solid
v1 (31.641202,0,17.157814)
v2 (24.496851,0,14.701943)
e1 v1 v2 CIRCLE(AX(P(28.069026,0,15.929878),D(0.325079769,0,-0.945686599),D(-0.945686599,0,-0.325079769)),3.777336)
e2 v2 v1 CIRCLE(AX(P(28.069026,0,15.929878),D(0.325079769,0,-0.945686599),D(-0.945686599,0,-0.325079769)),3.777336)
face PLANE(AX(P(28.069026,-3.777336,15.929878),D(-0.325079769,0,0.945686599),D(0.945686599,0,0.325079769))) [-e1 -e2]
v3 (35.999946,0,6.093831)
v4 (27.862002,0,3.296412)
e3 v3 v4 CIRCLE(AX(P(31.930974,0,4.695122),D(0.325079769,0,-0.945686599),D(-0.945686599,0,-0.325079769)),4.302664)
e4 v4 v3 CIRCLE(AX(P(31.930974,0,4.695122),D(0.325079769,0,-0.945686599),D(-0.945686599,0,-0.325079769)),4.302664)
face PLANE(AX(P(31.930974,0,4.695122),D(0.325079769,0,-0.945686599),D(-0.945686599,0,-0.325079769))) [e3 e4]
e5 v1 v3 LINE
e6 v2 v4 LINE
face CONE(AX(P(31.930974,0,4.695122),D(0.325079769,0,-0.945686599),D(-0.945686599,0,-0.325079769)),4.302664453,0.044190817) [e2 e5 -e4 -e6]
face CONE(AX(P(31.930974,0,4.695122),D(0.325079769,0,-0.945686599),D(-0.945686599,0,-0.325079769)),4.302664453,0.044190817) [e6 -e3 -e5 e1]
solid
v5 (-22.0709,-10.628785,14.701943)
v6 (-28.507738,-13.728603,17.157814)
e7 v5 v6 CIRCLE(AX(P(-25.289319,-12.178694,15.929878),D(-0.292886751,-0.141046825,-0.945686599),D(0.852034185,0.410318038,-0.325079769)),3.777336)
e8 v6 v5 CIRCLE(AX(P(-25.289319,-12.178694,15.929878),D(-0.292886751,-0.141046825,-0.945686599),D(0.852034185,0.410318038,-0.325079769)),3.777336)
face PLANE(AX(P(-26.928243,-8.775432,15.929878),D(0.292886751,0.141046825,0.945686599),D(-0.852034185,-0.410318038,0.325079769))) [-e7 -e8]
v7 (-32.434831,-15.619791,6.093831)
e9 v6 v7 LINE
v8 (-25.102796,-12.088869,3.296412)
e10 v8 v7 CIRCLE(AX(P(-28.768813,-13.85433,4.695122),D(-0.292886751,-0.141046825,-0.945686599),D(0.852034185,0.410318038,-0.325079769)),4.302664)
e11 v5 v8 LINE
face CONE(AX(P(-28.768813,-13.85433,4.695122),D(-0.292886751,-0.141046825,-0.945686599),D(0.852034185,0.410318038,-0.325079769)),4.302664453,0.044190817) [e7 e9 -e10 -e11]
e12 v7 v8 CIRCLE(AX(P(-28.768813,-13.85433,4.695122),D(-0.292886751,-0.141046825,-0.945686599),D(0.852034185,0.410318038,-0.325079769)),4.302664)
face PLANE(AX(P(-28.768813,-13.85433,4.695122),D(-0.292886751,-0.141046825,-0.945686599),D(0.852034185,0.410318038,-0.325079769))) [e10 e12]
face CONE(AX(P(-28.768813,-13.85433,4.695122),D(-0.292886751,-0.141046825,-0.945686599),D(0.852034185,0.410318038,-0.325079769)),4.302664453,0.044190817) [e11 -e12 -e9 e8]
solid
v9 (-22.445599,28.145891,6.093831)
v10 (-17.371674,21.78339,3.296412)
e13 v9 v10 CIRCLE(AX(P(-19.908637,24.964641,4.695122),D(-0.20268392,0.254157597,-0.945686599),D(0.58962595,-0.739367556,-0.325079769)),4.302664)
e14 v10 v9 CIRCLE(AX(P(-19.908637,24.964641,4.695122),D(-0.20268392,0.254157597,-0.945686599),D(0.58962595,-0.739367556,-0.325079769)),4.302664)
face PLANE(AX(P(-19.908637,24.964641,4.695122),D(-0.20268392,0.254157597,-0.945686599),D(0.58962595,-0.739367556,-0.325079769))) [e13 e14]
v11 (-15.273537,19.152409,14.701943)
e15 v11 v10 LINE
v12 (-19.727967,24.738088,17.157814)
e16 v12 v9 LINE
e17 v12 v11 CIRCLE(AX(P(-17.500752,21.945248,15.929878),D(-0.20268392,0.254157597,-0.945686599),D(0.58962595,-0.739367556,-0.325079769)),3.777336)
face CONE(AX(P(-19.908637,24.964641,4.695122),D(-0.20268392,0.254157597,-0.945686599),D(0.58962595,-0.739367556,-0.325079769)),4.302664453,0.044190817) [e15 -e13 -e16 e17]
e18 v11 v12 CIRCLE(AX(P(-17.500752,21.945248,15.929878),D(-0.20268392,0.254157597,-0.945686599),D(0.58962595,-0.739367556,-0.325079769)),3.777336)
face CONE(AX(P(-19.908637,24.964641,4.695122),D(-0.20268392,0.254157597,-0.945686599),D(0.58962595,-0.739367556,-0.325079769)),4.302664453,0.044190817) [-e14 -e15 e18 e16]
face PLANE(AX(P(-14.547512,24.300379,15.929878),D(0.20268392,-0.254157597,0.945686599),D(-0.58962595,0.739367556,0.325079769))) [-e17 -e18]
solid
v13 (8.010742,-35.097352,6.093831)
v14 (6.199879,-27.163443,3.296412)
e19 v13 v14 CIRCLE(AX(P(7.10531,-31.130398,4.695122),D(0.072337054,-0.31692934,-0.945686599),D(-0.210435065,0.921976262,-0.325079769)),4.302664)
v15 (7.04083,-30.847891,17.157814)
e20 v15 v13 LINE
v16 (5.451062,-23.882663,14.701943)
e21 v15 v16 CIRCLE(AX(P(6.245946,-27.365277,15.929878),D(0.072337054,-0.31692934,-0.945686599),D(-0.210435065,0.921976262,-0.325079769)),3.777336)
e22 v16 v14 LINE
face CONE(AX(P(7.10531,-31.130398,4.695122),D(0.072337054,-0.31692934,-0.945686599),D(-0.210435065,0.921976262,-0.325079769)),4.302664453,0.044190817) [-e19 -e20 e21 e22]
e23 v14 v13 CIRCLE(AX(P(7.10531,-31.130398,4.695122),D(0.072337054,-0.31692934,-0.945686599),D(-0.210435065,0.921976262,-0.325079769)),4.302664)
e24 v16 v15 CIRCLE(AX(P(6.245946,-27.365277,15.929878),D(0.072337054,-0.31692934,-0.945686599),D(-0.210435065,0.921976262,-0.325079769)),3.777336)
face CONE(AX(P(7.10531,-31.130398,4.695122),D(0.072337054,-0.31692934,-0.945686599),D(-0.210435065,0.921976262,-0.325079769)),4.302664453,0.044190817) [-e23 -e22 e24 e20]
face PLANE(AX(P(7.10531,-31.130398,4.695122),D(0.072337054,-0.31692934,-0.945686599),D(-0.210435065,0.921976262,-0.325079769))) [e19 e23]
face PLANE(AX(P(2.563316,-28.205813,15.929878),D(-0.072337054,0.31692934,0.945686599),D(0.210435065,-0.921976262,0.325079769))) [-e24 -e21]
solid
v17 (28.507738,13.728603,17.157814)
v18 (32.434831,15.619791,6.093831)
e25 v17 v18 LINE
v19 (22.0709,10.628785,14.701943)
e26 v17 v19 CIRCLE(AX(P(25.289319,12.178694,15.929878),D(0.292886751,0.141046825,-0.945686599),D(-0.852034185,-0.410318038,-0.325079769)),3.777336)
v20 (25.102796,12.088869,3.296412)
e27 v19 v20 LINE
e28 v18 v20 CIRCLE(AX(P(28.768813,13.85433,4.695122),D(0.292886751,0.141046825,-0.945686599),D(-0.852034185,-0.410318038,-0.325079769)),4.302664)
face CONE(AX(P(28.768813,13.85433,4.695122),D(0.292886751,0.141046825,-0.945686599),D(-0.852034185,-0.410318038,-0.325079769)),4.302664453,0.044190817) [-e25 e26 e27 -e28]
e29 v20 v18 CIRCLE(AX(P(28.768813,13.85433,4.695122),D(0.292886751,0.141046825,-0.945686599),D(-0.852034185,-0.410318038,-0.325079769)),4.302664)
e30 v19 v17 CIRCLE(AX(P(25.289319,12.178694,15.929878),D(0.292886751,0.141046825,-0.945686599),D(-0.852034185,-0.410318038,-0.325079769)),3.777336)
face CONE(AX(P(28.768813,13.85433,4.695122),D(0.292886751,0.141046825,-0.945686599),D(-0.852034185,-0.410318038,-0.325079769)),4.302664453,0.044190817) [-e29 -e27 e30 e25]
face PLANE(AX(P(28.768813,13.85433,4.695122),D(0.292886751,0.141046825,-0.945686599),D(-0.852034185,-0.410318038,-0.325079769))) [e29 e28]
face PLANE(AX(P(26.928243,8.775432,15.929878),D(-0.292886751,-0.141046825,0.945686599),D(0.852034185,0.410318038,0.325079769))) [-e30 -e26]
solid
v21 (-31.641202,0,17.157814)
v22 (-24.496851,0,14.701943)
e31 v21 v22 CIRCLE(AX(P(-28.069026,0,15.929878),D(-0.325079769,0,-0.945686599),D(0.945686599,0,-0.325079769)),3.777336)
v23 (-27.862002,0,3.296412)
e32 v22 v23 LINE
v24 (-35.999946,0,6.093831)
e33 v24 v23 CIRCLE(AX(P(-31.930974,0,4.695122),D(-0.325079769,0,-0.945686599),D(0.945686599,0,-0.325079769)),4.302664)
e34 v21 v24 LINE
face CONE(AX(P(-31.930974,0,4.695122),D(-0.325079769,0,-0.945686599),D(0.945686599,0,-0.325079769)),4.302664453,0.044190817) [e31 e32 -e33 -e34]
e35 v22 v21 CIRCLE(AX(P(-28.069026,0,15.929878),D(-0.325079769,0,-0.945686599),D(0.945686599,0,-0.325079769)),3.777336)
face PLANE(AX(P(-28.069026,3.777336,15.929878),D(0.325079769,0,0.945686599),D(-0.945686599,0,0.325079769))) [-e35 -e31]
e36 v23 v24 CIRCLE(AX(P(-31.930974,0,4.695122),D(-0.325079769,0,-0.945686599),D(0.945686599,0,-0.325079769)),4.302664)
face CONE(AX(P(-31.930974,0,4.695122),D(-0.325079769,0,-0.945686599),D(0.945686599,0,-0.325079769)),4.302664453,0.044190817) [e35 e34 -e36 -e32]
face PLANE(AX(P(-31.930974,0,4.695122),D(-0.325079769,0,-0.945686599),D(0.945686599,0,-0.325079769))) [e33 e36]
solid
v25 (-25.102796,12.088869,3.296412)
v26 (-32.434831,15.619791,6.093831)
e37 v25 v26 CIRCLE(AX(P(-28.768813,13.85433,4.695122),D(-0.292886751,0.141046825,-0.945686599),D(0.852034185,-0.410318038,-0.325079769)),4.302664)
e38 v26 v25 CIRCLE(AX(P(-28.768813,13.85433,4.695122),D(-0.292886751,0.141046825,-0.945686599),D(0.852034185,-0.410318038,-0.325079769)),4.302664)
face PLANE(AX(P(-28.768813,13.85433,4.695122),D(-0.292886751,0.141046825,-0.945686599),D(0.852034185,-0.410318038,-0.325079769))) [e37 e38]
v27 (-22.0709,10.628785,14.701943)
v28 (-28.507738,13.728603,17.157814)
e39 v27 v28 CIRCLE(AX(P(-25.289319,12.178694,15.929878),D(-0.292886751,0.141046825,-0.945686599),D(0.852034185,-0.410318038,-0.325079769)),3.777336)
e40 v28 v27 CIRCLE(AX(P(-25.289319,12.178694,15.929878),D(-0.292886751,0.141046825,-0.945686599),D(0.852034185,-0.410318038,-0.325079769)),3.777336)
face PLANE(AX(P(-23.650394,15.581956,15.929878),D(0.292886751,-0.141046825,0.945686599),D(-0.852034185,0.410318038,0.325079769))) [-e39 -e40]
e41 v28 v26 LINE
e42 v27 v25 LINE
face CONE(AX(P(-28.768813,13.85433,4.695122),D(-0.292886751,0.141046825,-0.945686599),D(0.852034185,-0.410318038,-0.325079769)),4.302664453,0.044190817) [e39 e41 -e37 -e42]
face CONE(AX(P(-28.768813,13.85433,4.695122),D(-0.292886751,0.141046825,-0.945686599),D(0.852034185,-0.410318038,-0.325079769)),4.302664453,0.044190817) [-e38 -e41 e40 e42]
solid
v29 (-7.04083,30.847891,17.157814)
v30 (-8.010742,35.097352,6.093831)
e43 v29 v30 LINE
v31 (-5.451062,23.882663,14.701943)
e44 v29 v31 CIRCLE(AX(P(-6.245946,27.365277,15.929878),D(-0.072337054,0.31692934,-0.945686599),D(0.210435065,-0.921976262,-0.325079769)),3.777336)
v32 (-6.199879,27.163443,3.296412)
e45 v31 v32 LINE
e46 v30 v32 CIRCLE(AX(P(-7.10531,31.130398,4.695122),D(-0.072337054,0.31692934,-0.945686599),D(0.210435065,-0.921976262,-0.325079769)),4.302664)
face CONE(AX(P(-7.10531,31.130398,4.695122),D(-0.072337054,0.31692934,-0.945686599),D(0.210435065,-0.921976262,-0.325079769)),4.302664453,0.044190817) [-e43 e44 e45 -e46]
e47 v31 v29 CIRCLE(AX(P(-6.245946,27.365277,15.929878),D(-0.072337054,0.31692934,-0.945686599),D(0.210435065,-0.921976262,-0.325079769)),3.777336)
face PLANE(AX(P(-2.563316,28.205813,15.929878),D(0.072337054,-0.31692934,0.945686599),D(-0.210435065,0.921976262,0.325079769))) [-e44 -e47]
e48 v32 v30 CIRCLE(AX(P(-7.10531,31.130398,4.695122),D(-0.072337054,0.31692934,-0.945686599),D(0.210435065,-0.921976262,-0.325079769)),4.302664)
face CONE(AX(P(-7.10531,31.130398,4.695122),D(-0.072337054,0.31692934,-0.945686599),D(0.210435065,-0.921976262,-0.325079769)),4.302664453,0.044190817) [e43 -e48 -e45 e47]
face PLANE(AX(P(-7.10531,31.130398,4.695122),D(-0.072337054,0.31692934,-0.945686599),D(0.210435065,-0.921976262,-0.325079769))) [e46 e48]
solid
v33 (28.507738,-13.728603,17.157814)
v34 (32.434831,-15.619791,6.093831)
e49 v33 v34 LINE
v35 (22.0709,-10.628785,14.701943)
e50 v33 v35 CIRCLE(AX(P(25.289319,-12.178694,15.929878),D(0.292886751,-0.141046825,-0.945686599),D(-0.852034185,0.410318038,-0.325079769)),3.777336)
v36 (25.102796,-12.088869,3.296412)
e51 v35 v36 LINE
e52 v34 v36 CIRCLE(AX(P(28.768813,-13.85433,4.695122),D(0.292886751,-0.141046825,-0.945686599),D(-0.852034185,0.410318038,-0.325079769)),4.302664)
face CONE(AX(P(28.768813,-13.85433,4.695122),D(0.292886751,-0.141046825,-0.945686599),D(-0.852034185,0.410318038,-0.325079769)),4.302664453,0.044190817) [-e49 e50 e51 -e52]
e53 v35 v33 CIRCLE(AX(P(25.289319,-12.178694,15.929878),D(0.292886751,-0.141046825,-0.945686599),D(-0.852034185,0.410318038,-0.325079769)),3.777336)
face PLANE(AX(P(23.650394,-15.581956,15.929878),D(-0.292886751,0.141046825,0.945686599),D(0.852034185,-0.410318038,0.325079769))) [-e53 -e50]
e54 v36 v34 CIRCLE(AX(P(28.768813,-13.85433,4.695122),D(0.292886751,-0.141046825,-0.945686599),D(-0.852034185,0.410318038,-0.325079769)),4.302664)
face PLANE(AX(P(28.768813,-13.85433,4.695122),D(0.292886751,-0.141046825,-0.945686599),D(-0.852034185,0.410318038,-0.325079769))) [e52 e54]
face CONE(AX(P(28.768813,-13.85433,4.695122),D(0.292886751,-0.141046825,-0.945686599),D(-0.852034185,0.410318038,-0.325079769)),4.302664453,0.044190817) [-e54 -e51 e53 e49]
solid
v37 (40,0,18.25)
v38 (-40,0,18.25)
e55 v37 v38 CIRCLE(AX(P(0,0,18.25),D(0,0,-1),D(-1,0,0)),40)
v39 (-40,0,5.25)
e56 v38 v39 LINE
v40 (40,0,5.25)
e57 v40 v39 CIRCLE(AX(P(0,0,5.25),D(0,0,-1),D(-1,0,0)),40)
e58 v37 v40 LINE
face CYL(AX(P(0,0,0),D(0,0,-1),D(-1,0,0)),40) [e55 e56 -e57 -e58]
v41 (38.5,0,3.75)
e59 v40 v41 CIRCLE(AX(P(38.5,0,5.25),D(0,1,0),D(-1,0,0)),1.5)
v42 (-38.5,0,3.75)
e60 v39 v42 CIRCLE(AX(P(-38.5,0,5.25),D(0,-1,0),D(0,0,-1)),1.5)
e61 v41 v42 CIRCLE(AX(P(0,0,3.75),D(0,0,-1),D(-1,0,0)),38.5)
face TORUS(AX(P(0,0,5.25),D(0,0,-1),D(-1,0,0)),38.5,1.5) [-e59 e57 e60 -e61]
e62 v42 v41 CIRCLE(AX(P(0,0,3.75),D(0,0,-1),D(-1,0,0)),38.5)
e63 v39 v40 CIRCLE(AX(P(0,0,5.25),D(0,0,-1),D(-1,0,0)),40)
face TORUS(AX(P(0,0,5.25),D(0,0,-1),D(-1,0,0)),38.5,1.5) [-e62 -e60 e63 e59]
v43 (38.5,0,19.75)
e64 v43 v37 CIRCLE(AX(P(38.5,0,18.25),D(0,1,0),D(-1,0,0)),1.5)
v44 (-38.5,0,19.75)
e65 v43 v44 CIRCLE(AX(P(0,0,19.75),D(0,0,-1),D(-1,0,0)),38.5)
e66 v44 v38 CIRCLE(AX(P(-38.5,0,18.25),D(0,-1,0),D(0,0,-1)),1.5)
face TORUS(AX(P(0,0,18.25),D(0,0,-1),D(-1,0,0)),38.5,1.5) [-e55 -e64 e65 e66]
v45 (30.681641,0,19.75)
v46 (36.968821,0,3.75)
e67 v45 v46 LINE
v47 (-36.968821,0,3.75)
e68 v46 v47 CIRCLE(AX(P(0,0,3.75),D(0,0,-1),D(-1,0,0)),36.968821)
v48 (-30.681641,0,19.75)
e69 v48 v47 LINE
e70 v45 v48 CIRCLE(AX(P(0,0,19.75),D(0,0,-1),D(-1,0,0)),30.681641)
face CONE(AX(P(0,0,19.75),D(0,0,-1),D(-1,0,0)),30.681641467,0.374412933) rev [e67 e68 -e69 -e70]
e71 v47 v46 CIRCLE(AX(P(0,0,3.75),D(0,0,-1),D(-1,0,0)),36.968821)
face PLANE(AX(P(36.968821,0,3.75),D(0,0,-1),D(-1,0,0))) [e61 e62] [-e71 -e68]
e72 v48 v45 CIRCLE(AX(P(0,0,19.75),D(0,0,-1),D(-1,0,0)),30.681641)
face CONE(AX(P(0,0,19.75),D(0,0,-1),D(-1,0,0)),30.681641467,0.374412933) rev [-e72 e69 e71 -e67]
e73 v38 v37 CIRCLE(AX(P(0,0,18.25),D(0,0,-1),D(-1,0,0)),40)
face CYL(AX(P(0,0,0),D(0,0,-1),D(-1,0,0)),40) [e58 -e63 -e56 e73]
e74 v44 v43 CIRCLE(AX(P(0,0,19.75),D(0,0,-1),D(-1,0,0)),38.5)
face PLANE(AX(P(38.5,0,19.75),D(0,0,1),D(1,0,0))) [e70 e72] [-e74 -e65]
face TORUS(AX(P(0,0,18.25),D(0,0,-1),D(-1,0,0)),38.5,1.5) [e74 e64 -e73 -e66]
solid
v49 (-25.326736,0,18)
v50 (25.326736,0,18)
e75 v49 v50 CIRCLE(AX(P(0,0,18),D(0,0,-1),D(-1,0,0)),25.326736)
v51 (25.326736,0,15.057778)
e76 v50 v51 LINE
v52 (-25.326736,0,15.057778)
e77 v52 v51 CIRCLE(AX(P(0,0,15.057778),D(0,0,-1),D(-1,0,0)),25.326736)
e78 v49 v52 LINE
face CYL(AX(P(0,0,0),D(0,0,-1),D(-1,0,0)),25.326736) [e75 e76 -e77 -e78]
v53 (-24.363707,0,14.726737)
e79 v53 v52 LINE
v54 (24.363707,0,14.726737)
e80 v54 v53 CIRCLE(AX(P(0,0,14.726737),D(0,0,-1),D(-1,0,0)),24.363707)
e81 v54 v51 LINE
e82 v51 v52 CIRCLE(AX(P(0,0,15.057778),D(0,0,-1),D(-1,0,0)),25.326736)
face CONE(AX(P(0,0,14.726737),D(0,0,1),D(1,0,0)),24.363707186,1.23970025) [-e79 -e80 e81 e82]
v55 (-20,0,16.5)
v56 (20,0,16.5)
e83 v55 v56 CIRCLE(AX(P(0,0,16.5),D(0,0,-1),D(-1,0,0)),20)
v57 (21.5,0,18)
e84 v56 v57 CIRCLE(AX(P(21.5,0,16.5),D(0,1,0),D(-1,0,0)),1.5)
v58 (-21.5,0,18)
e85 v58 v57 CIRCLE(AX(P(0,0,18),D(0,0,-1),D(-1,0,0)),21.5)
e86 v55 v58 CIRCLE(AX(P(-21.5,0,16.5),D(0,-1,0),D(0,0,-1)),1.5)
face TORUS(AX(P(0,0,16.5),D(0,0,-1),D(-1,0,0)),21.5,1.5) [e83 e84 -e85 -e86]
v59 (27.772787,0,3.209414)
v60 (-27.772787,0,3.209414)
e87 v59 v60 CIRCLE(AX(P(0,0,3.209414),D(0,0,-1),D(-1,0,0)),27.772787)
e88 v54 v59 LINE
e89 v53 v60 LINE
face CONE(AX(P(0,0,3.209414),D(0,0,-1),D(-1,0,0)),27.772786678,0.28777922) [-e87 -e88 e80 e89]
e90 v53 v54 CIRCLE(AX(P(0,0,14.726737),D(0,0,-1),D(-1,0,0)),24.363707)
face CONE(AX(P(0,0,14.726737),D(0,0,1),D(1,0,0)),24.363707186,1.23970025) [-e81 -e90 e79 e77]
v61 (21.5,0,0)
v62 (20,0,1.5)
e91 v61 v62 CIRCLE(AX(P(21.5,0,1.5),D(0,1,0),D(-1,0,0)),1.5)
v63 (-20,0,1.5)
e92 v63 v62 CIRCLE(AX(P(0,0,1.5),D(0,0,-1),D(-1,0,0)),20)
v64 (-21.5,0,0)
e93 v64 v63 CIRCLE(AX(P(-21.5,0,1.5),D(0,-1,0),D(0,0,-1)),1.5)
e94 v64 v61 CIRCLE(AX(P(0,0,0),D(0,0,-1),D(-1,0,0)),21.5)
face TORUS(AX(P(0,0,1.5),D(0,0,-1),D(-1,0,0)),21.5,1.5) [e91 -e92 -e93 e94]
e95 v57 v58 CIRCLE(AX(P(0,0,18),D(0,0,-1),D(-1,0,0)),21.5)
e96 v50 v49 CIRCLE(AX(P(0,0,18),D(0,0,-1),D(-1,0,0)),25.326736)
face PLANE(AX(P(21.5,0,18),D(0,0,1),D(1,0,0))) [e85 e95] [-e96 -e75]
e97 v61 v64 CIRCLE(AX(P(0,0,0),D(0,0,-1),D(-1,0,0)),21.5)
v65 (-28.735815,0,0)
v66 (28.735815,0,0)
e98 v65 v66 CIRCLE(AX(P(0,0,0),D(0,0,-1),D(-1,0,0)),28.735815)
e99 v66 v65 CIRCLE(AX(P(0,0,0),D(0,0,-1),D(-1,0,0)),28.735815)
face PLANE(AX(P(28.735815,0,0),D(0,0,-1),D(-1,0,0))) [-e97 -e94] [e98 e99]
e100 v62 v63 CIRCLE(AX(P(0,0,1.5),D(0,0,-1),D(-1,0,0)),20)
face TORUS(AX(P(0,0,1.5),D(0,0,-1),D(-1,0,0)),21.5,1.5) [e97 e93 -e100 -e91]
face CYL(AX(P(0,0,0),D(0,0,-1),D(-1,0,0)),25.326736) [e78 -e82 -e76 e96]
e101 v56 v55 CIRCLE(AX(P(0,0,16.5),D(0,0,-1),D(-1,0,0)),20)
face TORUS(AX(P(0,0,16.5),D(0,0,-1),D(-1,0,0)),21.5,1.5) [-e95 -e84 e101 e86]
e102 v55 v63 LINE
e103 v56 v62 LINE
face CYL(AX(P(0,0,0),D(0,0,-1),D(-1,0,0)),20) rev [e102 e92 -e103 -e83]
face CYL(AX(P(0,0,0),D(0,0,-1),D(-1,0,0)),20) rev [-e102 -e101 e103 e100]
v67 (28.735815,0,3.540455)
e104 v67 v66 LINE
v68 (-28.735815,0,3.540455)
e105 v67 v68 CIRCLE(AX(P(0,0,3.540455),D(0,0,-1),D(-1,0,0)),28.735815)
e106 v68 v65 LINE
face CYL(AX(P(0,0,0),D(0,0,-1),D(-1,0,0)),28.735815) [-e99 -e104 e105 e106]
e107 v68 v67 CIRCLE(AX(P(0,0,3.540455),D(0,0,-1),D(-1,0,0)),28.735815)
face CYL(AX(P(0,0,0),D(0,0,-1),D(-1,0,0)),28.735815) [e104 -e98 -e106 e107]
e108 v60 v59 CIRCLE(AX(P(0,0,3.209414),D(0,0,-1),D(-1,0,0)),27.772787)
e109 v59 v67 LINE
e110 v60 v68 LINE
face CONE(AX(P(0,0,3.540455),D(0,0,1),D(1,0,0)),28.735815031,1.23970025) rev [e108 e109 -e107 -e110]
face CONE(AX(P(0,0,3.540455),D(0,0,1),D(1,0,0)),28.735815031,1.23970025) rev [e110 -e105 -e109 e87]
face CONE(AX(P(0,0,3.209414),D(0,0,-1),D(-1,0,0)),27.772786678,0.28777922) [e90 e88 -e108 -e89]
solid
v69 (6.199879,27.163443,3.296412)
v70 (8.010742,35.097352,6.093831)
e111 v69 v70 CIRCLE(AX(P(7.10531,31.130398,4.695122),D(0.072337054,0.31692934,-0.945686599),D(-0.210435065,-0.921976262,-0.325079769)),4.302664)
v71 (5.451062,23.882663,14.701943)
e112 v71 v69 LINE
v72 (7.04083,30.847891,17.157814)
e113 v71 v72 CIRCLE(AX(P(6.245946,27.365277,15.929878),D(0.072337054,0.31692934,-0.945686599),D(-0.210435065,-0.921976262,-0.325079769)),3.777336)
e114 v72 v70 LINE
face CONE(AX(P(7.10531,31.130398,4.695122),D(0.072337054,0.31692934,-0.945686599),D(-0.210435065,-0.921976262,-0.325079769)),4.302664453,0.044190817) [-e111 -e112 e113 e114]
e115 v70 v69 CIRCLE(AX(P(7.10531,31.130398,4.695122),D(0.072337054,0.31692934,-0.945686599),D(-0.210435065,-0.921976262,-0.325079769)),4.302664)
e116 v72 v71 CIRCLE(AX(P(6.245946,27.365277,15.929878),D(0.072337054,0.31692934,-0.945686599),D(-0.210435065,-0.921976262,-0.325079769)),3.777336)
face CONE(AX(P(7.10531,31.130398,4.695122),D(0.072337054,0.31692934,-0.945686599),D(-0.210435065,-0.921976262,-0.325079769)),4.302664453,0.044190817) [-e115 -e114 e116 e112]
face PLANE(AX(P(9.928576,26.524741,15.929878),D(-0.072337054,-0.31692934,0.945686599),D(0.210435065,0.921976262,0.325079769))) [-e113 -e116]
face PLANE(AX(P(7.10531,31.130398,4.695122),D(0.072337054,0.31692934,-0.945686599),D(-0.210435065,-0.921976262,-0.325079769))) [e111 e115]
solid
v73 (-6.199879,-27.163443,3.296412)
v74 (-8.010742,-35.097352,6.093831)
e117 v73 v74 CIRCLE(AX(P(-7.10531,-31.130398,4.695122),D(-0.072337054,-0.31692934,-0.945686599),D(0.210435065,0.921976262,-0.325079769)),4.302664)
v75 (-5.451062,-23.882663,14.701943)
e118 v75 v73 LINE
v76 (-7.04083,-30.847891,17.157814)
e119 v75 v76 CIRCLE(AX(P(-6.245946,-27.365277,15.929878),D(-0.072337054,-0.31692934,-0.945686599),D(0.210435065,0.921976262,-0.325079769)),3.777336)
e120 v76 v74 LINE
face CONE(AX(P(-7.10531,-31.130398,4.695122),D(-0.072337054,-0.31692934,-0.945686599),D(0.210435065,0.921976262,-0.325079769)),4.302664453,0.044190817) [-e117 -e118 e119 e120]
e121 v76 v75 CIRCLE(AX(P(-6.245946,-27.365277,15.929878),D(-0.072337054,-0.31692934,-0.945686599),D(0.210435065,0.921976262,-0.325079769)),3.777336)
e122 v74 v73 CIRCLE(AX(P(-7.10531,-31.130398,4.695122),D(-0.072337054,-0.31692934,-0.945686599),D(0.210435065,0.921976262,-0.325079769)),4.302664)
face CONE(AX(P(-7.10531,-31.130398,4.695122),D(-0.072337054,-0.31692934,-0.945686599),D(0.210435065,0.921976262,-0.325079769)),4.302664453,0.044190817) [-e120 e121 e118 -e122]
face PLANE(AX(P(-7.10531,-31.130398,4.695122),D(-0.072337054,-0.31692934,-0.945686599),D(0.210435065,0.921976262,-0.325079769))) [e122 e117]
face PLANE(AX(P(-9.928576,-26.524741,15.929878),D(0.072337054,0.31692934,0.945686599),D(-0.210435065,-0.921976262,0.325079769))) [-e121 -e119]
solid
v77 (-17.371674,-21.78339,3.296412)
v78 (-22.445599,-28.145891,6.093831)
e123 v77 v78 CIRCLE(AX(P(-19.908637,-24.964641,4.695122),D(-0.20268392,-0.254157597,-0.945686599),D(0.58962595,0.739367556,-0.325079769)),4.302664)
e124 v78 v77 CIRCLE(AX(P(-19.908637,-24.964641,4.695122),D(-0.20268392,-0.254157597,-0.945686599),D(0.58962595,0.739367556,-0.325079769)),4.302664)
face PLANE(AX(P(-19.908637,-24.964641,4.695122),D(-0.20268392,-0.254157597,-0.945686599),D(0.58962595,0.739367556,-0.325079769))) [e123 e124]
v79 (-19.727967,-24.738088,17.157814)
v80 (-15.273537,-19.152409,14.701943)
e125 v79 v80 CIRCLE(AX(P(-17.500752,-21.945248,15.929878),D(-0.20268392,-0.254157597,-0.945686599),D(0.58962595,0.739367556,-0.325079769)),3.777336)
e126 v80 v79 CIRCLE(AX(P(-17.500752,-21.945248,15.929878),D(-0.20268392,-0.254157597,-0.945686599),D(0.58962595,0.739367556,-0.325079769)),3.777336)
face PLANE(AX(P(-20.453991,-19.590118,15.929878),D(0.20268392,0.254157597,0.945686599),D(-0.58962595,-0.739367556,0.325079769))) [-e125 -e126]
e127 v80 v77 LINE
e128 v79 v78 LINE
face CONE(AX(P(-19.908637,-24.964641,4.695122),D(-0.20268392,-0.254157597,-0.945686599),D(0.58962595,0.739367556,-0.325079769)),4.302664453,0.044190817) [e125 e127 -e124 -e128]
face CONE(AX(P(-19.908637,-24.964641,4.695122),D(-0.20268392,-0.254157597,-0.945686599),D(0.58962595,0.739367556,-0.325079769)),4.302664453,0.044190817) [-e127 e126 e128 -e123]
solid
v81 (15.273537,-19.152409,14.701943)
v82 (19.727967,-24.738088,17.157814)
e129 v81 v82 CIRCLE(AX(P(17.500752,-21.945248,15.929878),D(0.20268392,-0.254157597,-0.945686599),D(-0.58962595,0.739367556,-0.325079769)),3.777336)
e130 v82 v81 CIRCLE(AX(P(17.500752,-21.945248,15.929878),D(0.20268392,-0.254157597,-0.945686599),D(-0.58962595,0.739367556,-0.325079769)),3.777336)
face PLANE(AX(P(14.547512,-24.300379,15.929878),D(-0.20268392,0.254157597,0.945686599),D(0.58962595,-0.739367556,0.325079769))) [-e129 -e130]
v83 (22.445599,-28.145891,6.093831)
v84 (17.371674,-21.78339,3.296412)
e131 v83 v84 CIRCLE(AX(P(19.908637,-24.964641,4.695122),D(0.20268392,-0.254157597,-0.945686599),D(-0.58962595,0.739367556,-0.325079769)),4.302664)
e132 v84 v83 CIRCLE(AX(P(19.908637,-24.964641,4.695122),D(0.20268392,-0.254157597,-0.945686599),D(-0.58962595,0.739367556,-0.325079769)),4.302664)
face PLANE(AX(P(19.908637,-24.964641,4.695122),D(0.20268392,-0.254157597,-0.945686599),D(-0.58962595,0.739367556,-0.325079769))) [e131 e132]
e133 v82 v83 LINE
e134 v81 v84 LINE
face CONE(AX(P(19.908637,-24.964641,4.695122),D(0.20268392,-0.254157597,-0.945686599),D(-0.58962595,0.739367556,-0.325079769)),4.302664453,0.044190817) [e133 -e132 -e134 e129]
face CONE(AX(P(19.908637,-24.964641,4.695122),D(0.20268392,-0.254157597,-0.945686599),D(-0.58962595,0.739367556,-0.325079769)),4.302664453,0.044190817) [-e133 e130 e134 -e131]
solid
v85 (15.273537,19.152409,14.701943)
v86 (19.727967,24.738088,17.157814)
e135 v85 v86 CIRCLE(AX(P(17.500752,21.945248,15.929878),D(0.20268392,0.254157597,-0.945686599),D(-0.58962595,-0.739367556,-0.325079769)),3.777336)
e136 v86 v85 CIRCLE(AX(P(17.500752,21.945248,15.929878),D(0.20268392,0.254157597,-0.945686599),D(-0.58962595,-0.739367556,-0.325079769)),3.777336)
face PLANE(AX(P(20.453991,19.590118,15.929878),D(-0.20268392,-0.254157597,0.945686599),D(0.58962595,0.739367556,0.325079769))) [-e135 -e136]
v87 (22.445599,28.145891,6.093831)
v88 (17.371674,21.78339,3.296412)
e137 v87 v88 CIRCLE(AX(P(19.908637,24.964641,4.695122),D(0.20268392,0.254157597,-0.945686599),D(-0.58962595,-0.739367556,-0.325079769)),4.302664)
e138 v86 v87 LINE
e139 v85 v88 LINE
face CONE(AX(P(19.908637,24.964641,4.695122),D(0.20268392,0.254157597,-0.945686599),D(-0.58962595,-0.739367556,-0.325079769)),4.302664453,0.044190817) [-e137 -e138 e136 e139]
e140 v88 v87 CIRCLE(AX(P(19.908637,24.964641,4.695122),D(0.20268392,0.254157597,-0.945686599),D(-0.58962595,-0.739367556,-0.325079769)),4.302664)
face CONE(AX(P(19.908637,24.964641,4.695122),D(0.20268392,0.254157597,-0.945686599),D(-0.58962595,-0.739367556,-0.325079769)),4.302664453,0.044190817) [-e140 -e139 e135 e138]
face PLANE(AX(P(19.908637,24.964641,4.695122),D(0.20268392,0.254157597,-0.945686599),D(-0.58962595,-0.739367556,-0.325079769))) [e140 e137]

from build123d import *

# Parameters (mm, degrees)
PATTERN_CIRCULAR_1_COUNT = 14


with BuildPart() as part:
    # 草图1 → 旋转1 (revolve)
    with BuildSketch(Plane.XZ, mode=Mode.PRIVATE) as revolve_1_sk:
        with BuildLine():
            Line((28.735815031, 0), (21.5, 0))
            ThreePointArc((21.5, 0), (20.439339828, 0.439339828), (20, 1.5))
            Line((20, 1.5), (20, 16.5))
            ThreePointArc((20, 16.5), (20.439339828, 17.560660172), (21.5, 18))
            Line((21.5, 18), (25.326735538, 18))
            Line((25.326735538, 18), (25.326735538, 15.057777647))
            Line((25.326735538, 15.057777647), (24.363707186, 14.726736651))
            Line((24.363707186, 14.726736651), (27.772786678, 3.20941449))
            Line((27.772786678, 3.20941449), (28.735815031, 3.540455486))
            Line((28.735815031, 3.540455486), (28.735815031, 0))
        make_face()
    revolve(revolve_1_sk.sketch.rotate(Axis((0, 0, 0), (0, 0, 1)), 180), axis=Axis((0, 0, 0), (0, 0, 1)))


with BuildPart() as body_2:
    # 草图2 → 旋转2 (revolve)
    with BuildSketch(Plane(origin=(30, 0, 10.3125), x_dir=(0, -1, 0), z_dir=(-0.9456865993048664, 0, -0.3250797685110486)), mode=Mode.PRIVATE) as revolve_2_sk:
        Polygon((0, -5.94), (4.302664453, -5.94), (3.777335547, 5.94), (0, 5.94), align=None)
    revolve(revolve_2_sk.sketch.rotate(Axis((30, 0, 10.3125), (-0.32507976851104853, 0, 0.9456865993048665)), 270), axis=Axis((30, 0, 10.3125), (-0.32507976851104853, 0, 0.9456865993048665)))


with BuildPart() as body_3:
    # 草图3 → 旋转3 (revolve)
    with BuildSketch(Plane.XZ, mode=Mode.PRIVATE) as revolve_3_sk:
        with BuildLine():
            Line((36.968820734, 3.75), (38.500000001, 3.75))
            ThreePointArc((38.500000001, 3.75), (39.560660173, 4.189339828), (40.000000001, 5.25))
            Line((40.000000001, 5.25), (40.000000001, 18.25))
            ThreePointArc((40.000000001, 18.25), (39.560660173, 19.310660172), (38.500000001, 19.75))
            Line((38.500000001, 19.75), (30.681641467, 19.75))
            Line((30.681641467, 19.75), (36.968820734, 3.75))
        make_face()
    revolve(revolve_3_sk.sketch.rotate(Axis((0, 0, 0), (0, 0, 1)), 180), axis=Axis((0, 0, 0), (0, 0, 1)))


with BuildPart() as pattern_circular_1_1:
    # 阵列(圆周)1: pattern copy
    add(body_2.part.rotate(Axis((0, 0, 0), (0, 0, 1)), 1 * 360 / PATTERN_CIRCULAR_1_COUNT))


with BuildPart() as pattern_circular_1_2:
    # 阵列(圆周)1: pattern copy
    add(body_2.part.rotate(Axis((0, 0, 0), (0, 0, 1)), 2 * 360 / PATTERN_CIRCULAR_1_COUNT))


with BuildPart() as pattern_circular_1_3:
    # 阵列(圆周)1: pattern copy
    add(body_2.part.rotate(Axis((0, 0, 0), (0, 0, 1)), 3 * 360 / PATTERN_CIRCULAR_1_COUNT))


with BuildPart() as pattern_circular_1_4:
    # 阵列(圆周)1: pattern copy
    add(body_2.part.rotate(Axis((0, 0, 0), (0, 0, 1)), 4 * 360 / PATTERN_CIRCULAR_1_COUNT))


with BuildPart() as pattern_circular_1_5:
    # 阵列(圆周)1: pattern copy
    add(body_2.part.rotate(Axis((0, 0, 0), (0, 0, 1)), 5 * 360 / PATTERN_CIRCULAR_1_COUNT))


with BuildPart() as pattern_circular_1_6:
    # 阵列(圆周)1: pattern copy
    add(body_2.part.rotate(Axis((0, 0, 0), (0, 0, 1)), 6 * 360 / PATTERN_CIRCULAR_1_COUNT))


with BuildPart() as pattern_circular_1_7:
    # 阵列(圆周)1: pattern copy
    add(body_2.part.rotate(Axis((0, 0, 0), (0, 0, 1)), 7 * 360 / PATTERN_CIRCULAR_1_COUNT))


with BuildPart() as pattern_circular_1_8:
    # 阵列(圆周)1: pattern copy
    add(body_2.part.rotate(Axis((0, 0, 0), (0, 0, 1)), 8 * 360 / PATTERN_CIRCULAR_1_COUNT))


with BuildPart() as pattern_circular_1_9:
    # 阵列(圆周)1: pattern copy
    add(body_2.part.rotate(Axis((0, 0, 0), (0, 0, 1)), 9 * 360 / PATTERN_CIRCULAR_1_COUNT))


with BuildPart() as pattern_circular_1_10:
    # 阵列(圆周)1: pattern copy
    add(body_2.part.rotate(Axis((0, 0, 0), (0, 0, 1)), 10 * 360 / PATTERN_CIRCULAR_1_COUNT))


with BuildPart() as pattern_circular_1_11:
    # 阵列(圆周)1: pattern copy
    add(body_2.part.rotate(Axis((0, 0, 0), (0, 0, 1)), 11 * 360 / PATTERN_CIRCULAR_1_COUNT))


with BuildPart() as pattern_circular_1_12:
    # 阵列(圆周)1: pattern copy
    add(body_2.part.rotate(Axis((0, 0, 0), (0, 0, 1)), 12 * 360 / PATTERN_CIRCULAR_1_COUNT))


with BuildPart() as pattern_circular_1_13:
    # 阵列(圆周)1: pattern copy
    add(body_2.part.rotate(Axis((0, 0, 0), (0, 0, 1)), 13 * 360 / PATTERN_CIRCULAR_1_COUNT))


solid = Compound([part.part, body_2.part, body_3.part, pattern_circular_1_1.part, pattern_circular_1_2.part, pattern_circular_1_3.part, pattern_circular_1_4.part, pattern_circular_1_5.part, pattern_circular_1_6.part, pattern_circular_1_7.part, pattern_circular_1_8.part, pattern_circular_1_9.part, pattern_circular_1_10.part, pattern_circular_1_11.part, pattern_circular_1_12.part, pattern_circular_1_13.part])
